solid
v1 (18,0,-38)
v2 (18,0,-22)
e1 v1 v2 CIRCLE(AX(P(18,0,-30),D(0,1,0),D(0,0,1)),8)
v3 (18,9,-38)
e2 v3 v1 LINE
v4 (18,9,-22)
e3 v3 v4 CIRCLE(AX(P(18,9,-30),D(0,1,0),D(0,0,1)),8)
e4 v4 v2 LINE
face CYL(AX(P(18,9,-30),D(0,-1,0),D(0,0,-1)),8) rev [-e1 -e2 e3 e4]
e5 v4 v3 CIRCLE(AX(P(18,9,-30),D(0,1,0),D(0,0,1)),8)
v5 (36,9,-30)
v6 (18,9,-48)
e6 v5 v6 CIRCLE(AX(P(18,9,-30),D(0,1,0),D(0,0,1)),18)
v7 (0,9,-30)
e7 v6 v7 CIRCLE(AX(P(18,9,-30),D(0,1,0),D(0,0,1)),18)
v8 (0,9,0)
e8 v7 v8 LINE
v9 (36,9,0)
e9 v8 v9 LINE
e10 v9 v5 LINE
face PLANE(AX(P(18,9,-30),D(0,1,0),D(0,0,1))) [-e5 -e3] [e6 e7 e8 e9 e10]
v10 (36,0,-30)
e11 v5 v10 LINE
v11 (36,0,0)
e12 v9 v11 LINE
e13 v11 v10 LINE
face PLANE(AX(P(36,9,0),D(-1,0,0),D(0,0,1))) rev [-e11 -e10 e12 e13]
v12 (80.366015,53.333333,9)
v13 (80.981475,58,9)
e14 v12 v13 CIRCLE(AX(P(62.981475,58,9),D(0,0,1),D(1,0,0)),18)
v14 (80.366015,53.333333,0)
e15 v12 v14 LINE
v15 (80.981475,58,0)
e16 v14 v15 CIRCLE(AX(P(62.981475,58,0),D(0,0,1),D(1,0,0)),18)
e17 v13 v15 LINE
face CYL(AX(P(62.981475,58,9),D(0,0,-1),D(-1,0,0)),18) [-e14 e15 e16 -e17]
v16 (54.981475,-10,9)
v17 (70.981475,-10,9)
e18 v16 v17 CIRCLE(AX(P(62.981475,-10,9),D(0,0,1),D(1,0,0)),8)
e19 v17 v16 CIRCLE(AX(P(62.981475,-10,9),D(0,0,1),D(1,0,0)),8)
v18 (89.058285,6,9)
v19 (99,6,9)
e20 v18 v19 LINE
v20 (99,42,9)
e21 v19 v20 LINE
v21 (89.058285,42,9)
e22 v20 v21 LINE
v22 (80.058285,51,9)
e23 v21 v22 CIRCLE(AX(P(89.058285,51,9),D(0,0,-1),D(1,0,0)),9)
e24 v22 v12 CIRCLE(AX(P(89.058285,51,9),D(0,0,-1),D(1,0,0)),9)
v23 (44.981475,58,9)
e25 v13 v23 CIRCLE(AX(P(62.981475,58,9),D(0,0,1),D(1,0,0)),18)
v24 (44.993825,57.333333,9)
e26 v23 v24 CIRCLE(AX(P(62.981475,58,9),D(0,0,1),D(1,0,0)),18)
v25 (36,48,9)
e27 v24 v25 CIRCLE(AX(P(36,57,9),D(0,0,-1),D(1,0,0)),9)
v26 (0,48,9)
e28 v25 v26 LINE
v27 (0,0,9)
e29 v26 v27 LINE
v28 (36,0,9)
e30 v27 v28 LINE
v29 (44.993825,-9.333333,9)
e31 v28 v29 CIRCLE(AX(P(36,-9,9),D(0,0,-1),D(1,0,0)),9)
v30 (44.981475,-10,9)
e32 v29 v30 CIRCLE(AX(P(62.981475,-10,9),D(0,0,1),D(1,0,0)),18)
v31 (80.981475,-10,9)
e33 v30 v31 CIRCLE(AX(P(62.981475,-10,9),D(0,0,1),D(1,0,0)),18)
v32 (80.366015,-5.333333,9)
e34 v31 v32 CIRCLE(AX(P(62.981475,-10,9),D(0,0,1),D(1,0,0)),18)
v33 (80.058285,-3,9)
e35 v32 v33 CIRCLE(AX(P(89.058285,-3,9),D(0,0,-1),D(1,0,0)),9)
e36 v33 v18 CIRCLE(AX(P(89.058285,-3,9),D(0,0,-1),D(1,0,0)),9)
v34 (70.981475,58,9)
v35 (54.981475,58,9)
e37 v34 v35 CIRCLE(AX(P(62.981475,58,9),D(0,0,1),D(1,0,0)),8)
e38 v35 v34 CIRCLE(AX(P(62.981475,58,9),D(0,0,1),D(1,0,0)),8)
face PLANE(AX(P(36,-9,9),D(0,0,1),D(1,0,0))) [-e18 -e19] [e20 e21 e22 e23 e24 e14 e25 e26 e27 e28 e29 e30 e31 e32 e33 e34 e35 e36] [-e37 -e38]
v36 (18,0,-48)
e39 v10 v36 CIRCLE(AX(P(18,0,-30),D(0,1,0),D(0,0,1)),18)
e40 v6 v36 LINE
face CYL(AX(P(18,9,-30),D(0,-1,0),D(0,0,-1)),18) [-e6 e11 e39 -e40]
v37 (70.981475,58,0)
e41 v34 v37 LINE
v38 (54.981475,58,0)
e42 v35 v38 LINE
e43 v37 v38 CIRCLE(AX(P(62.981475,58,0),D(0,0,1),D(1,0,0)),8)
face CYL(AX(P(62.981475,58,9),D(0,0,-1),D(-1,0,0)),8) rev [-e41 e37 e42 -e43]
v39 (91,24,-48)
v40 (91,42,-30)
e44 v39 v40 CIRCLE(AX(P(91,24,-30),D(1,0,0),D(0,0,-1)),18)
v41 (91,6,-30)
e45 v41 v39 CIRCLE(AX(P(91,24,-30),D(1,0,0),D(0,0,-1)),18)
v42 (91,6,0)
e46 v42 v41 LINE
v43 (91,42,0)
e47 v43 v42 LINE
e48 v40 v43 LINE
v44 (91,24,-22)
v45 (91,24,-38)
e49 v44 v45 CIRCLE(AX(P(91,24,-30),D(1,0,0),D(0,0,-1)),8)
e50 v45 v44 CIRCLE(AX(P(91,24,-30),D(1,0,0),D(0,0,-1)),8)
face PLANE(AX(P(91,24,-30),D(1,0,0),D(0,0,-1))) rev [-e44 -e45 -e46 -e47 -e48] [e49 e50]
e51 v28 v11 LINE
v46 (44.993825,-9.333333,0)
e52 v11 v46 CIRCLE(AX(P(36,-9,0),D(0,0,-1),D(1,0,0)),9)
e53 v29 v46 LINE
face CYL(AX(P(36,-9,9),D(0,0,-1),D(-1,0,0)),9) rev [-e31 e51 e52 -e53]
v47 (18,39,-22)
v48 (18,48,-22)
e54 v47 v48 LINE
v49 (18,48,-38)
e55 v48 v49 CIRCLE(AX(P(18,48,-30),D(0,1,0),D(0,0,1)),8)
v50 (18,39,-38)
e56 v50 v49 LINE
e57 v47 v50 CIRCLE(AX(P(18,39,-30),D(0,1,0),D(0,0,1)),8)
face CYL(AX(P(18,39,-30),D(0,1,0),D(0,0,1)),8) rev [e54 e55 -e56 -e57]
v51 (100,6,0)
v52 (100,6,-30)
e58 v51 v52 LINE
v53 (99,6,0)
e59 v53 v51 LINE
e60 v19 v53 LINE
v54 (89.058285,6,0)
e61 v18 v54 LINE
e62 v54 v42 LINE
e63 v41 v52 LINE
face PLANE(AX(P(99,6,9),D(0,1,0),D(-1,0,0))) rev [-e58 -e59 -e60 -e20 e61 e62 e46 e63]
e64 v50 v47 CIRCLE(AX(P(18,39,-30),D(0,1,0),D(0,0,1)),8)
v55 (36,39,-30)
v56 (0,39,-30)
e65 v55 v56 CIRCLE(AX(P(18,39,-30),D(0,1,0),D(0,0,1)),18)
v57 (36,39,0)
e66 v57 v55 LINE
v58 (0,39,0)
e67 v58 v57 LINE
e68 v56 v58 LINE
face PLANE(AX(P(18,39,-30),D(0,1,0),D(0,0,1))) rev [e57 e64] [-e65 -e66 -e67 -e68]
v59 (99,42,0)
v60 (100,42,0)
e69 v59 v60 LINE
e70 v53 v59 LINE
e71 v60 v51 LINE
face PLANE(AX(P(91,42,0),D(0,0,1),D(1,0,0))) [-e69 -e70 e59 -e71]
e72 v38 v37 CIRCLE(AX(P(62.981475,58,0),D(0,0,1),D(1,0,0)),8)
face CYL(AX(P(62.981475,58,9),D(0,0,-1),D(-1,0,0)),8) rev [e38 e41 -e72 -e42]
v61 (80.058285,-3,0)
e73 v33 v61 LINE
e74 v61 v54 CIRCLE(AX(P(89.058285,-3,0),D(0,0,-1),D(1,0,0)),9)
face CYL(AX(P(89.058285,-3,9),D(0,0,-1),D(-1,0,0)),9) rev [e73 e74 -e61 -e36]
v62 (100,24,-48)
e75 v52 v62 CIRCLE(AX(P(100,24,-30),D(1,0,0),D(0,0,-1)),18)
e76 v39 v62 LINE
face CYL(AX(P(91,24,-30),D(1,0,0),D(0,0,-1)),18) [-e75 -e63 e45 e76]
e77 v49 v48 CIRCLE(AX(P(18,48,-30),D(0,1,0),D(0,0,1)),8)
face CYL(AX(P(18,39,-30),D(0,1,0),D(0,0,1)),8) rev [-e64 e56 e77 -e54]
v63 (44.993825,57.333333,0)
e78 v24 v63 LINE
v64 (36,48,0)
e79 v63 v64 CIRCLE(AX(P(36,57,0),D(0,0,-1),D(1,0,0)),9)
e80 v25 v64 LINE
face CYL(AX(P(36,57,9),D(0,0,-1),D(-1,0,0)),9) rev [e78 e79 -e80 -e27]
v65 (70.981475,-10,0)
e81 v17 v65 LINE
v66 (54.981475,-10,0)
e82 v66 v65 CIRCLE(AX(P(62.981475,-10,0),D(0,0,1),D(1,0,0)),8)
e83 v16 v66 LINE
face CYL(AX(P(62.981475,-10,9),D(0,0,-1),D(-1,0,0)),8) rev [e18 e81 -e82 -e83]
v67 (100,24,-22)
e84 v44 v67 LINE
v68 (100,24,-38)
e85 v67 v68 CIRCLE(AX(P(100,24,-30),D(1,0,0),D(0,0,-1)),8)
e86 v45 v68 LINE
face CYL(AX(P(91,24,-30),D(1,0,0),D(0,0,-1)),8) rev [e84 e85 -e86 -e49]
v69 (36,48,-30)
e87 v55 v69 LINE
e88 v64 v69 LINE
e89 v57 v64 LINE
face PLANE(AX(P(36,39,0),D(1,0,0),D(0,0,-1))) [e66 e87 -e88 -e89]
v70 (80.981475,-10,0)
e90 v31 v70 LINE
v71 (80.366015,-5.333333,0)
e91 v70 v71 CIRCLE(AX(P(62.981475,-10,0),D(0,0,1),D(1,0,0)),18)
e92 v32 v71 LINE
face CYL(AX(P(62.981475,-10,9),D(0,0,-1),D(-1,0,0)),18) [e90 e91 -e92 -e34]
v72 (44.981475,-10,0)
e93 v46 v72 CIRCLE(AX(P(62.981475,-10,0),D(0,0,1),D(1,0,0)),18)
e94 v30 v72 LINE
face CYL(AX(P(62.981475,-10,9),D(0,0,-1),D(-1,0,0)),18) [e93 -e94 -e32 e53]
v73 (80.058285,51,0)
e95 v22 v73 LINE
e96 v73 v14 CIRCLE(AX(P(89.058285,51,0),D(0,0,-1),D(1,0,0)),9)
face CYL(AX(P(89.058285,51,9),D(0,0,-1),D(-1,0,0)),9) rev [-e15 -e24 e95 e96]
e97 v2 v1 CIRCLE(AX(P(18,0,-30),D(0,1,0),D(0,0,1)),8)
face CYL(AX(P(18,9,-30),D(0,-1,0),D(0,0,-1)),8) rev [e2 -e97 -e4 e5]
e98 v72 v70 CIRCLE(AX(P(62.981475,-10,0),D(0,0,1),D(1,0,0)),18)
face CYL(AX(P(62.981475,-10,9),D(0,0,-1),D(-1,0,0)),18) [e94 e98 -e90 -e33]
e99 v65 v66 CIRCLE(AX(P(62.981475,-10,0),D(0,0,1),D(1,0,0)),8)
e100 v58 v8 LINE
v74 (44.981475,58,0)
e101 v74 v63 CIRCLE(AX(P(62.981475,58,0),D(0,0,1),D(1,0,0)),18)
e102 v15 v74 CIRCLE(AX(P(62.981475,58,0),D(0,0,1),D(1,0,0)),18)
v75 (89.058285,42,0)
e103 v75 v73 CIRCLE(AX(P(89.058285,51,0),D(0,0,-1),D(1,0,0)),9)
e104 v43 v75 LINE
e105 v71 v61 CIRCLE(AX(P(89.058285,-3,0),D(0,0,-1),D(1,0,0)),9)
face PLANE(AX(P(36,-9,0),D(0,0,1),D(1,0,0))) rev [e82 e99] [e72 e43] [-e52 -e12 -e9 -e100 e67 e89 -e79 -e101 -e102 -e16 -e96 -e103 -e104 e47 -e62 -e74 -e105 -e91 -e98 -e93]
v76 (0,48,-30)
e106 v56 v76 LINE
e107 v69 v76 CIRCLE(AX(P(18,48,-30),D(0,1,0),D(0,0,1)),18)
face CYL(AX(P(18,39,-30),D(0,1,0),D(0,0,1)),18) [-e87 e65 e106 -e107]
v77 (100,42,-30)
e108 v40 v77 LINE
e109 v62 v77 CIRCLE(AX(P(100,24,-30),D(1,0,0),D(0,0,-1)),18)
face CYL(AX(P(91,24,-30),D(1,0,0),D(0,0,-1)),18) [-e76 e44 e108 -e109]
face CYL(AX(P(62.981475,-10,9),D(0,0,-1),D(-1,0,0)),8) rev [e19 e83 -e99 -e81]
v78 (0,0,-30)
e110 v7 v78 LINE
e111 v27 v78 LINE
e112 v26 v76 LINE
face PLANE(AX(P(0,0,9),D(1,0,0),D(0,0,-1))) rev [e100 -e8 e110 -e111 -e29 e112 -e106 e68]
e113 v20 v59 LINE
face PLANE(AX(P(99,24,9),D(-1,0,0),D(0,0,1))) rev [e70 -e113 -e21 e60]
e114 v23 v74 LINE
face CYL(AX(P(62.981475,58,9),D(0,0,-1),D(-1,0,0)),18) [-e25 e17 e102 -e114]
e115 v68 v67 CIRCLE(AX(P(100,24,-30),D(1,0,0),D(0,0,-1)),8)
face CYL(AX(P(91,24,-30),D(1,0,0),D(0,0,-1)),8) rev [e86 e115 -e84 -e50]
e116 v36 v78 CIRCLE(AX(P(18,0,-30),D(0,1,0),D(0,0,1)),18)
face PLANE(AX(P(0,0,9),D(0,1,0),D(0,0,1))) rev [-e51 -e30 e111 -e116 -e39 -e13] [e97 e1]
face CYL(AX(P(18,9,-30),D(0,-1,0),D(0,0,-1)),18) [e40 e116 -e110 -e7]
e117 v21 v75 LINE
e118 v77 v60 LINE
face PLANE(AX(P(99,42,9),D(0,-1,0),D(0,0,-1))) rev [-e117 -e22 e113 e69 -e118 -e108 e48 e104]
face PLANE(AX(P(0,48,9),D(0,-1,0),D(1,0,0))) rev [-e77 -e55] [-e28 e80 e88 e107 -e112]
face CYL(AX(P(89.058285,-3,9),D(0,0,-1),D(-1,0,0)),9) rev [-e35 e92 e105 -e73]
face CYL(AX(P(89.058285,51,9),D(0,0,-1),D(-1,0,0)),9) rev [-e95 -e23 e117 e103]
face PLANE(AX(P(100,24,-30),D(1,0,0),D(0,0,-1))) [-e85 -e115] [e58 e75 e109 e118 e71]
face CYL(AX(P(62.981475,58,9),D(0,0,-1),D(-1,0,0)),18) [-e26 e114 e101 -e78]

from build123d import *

# Parameters (mm, degrees)
BASE_PLATE_PROFILE_SKETCH_R = 8
BASE_PLATE_9MM_DEPTH        = 9
LUG_SKETCH_X100_R           = 8
LUG_X100_DEPTH              = 9
LUG_SKETCH_X0_R             = 8
LUG_X0_DEPTH                = 9
LUG_START                   = -9
LUG_SKETCH_OFFSET_48_R      = 8
LUG_OFFSET_48_DEPTH         = 9


with BuildPart() as part:
    # Base Plate Profile Sketch → Base Plate 9mm (new body)
    with BuildSketch(Plane.XY):
        with BuildLine():
            Line((0, 0), (0, 48))
            Line((0, 48), (36, 48))
            ThreePointArc((36, 48), (42.480740698, 50.755002002), (44.993825042, 57.333333333))
            ThreePointArc((44.993825042, 57.333333333), (65.004081247, 75.886001914), (80.366014874, 53.333333333))
            ThreePointArc((80.366014874, 53.333333333), (81.916856319, 45.522774425), (89.058284747, 42))
            Line((89.058284747, 42), (99, 42))
            Line((99, 42), (99, 24))
            Line((99, 24), (99, 6))
            Line((99, 6), (89.058284747, 6))
            ThreePointArc((89.058284747, 6), (81.916856319, 2.477225575), (80.366014874, -5.333333333))
            ThreePointArc((80.366014874, -5.333333333), (65.004081247, -27.886001914), (44.993825042, -9.333333333))
            ThreePointArc((44.993825042, -9.333333333), (42.480740698, -2.755002002), (36, 0))
            Line((36, 0), (0, 0))
        make_face()
        with Locations((62.981475126, 58)):
            Circle(BASE_PLATE_PROFILE_SKETCH_R, mode=Mode.SUBTRACT)
        with Locations((62.981475126, -10)):
            Circle(BASE_PLATE_PROFILE_SKETCH_R, mode=Mode.SUBTRACT)
    extrude(amount=BASE_PLATE_9MM_DEPTH)

    # Lug Sketch X100 → Lug X100 (add)
    with BuildSketch(Plane(origin=(100, 0, 0), x_dir=(0, 0, -1), z_dir=(1, 0, 0))):
        with BuildLine():
            Line((30, 42), (0, 42))
            Line((0, 42), (0, 6))
            Line((0, 6), (30, 6))
            ThreePointArc((30, 6), (48, 24), (30, 42))
        make_face()
        with Locations((30, 24)):
            Circle(LUG_SKETCH_X100_R, mode=Mode.SUBTRACT)
    extrude(amount=-LUG_X100_DEPTH)

    # Lug Sketch X0 → Lug X0 (add)
    with BuildSketch(Plane(origin=(0, 0, 0), x_dir=(1, 0, 0), z_dir=(0, 1, 0))):
        with BuildLine():
            Line((0, 30), (0, 0))
            Line((0, 0), (36, 0))
            Line((36, 0), (36, 30))
            ThreePointArc((36, 30), (18, 48), (0, 30))
        make_face()
        with Locations(Location((18, 30, 0), (0, 0, 270))):
            Circle(LUG_SKETCH_X0_R, mode=Mode.SUBTRACT)
    extrude(amount=LUG_X0_DEPTH)

    # Lug Sketch Offset 48 → Lug Offset 48 (add)
    with BuildSketch(Plane(origin=(0, 48, 0), x_dir=(1, 0, 0), z_dir=(0, 1, 0)).offset(LUG_START)):
        with BuildLine():
            Line((0, 30), (0, 0))
            Line((0, 0), (36, 0))
            Line((36, 0), (36, 30))
            ThreePointArc((36, 30), (18, 48), (0, 30))
        make_face()
        with Locations(Location((18, 30, 0), (0, 0, 270))):
            Circle(LUG_SKETCH_OFFSET_48_R, mode=Mode.SUBTRACT)
    extrude(amount=LUG_OFFSET_48_DEPTH)


solid = part.part
